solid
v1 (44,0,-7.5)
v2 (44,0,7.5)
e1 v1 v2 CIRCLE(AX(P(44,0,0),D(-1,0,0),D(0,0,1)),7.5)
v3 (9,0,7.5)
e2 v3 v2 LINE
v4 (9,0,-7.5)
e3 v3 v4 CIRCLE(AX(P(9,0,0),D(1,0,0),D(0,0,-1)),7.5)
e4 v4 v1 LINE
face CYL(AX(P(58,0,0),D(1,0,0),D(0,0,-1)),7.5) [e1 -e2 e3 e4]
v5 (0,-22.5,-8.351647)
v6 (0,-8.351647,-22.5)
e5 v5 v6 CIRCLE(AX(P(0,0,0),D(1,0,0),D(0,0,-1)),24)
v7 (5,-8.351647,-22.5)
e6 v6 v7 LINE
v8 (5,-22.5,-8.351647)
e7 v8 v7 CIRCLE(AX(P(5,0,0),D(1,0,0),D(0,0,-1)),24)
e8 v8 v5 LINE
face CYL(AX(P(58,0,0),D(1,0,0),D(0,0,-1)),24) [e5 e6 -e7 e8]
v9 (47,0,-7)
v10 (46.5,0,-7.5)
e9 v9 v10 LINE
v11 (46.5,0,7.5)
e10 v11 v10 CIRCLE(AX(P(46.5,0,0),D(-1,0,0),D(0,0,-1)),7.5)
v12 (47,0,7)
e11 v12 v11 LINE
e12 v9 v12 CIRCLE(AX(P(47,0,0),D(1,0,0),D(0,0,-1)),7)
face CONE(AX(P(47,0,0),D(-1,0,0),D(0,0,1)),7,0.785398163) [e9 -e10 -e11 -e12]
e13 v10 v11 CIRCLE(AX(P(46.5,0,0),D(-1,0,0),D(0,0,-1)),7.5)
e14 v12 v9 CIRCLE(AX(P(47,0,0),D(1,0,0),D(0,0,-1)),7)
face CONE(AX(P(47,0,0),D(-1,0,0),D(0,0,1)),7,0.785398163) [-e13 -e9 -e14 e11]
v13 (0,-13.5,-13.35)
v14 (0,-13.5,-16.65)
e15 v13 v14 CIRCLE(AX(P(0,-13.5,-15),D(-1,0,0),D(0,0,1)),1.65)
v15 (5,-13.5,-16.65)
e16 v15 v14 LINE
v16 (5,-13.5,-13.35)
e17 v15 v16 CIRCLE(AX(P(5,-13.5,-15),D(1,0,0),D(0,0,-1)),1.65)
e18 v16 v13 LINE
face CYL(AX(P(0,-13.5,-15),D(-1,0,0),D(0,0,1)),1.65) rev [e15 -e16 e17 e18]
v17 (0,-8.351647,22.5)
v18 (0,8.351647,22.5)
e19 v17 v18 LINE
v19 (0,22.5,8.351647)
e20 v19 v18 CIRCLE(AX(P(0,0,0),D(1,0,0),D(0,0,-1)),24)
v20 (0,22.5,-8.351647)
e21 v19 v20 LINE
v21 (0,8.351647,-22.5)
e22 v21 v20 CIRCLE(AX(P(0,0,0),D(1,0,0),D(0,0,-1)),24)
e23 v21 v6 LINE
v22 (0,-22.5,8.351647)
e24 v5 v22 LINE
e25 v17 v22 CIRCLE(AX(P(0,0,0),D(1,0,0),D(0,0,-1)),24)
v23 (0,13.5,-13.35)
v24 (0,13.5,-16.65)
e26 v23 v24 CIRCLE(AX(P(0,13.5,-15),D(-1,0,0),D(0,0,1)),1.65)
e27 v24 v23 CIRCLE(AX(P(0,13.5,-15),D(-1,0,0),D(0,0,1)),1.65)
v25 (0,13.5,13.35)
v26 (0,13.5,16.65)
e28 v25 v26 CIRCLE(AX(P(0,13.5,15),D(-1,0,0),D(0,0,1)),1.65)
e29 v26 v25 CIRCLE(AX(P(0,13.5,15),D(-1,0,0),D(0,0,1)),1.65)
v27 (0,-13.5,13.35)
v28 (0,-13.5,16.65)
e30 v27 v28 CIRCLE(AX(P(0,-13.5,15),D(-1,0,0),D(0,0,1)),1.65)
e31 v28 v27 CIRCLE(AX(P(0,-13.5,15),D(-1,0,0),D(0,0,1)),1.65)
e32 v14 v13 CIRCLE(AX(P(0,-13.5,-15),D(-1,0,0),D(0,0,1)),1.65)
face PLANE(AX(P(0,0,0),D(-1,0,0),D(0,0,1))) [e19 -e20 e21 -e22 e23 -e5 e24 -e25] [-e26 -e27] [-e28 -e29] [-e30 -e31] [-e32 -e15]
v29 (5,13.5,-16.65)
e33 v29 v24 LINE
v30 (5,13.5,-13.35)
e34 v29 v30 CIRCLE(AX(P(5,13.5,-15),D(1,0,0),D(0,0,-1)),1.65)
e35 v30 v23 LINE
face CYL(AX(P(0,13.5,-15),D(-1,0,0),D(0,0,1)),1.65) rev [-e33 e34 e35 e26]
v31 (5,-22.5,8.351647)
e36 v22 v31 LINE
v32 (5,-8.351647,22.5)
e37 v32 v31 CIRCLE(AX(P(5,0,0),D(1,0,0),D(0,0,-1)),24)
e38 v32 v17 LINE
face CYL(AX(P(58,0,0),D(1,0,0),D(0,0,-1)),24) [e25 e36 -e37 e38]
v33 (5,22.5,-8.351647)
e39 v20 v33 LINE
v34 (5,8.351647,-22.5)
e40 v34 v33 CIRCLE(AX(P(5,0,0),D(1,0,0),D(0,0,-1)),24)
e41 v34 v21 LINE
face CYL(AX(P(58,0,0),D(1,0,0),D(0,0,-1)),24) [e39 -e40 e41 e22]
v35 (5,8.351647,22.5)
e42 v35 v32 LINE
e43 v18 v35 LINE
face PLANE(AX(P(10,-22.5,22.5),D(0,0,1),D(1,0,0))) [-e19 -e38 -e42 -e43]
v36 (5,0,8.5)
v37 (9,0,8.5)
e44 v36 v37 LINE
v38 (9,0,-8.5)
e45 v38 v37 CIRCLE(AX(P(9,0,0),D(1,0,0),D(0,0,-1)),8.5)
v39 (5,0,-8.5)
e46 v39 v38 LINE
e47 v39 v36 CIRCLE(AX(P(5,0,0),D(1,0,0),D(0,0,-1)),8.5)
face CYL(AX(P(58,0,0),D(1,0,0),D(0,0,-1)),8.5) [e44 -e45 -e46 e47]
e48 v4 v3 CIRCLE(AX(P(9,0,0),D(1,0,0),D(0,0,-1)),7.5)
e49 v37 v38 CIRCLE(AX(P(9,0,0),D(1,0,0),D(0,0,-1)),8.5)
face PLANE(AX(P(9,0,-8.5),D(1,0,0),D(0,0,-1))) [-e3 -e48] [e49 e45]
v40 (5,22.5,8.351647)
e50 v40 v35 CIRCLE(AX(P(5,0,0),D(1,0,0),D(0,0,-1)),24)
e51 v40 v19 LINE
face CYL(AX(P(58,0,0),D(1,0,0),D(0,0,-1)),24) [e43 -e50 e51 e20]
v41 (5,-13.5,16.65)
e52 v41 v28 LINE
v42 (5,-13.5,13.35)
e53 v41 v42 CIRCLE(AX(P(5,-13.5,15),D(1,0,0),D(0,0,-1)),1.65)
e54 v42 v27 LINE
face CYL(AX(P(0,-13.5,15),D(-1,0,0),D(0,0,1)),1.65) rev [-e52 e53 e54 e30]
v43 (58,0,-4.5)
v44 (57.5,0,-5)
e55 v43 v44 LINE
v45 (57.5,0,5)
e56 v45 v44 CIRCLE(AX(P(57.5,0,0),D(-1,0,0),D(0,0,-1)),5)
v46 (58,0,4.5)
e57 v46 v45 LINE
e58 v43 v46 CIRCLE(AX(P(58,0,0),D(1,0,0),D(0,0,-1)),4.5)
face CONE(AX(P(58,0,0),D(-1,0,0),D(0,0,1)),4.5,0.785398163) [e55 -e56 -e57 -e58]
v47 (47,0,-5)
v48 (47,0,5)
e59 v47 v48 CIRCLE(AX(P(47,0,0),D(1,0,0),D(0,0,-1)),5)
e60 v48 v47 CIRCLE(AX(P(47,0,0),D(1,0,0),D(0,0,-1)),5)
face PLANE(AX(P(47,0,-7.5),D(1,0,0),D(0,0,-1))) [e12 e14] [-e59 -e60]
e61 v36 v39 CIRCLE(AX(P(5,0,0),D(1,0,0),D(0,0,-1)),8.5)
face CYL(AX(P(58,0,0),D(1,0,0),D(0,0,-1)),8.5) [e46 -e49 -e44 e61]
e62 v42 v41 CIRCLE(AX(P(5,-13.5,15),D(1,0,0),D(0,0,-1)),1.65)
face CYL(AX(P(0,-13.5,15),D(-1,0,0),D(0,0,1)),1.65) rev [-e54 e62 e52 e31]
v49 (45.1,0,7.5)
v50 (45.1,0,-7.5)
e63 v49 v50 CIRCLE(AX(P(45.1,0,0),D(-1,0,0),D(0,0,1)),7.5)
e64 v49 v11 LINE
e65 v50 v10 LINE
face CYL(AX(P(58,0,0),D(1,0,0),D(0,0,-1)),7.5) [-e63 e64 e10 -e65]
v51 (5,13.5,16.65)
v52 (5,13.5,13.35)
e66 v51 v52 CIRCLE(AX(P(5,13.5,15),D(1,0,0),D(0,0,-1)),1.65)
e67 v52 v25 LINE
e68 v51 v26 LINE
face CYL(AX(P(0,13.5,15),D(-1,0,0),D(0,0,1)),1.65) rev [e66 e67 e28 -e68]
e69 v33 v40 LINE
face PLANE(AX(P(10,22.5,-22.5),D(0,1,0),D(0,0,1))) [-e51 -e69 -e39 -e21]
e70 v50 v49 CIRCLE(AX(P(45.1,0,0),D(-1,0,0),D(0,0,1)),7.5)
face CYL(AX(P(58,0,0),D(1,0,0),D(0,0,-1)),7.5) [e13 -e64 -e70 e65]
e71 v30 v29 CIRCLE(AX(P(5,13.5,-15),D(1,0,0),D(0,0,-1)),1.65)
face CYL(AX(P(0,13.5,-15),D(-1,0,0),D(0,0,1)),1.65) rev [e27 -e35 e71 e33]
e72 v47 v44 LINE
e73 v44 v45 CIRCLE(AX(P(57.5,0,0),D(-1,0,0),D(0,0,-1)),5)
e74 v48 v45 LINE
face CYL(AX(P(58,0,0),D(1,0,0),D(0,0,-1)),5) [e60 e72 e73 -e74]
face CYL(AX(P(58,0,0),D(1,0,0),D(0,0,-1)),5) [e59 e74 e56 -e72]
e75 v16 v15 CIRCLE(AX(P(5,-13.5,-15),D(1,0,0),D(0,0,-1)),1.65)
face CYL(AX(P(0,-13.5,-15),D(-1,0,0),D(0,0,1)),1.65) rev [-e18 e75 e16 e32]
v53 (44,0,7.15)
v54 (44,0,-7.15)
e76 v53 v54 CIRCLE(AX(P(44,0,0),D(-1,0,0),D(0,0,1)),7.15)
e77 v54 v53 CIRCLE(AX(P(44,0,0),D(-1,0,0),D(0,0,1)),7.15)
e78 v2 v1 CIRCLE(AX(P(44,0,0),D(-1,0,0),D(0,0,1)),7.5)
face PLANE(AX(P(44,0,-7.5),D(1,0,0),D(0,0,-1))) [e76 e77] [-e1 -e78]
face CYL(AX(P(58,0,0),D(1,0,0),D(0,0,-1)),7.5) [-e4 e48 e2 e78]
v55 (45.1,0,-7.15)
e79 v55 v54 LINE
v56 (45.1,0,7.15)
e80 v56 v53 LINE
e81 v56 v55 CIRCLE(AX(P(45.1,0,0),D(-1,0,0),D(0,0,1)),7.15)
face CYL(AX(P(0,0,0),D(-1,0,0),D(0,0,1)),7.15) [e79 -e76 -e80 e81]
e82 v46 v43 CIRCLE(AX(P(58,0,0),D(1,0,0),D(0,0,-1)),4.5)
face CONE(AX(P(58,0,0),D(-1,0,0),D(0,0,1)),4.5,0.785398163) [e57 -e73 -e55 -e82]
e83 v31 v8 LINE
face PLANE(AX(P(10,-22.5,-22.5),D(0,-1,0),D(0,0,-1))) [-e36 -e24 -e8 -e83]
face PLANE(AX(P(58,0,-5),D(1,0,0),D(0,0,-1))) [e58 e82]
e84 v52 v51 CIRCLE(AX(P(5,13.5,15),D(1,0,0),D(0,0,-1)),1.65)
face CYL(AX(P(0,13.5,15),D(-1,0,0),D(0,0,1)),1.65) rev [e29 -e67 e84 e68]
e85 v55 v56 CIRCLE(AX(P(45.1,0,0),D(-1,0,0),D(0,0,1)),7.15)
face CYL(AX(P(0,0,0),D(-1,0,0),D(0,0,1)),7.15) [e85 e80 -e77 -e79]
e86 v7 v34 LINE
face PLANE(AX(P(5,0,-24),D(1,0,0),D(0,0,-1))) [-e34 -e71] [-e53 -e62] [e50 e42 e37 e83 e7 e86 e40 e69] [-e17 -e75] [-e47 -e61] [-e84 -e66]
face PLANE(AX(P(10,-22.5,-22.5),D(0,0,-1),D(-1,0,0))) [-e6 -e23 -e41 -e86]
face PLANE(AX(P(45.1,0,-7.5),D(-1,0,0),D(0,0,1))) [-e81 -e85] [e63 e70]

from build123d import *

# Parameters (mm, degrees)
HOLE_WIZARD_M4_1_D   = 3.3
SKETCH_4_OUTSIDE_W   = 67.858
SKETCH_4_OUTSIDE_H   = 67.858
SKETCH_4_OUTSIDE_W_2 = 45
SKETCH_4_OUTSIDE_H_2 = 45
CUT_EXTRUDE_1_DEPTH  = 10
CHAMFER_1_SIZE       = 0.5
SKETCH_5_W           = 1.1
SKETCH_5_H           = 0.35


with BuildPart() as part:
    # 草图1 → 旋转1 (revolve)
    with BuildSketch(Plane(origin=(0, 0, 0), x_dir=(1, 0, 0), z_dir=(0, 1, 0))):
        Polygon((0, 0), (0, 24), (5, 24), (5, 8.5), (9, 8.5), (9, 7.5), (47, 7.5), (47, 5), (58, 5), (58, 0), align=None)
    revolve(axis=Axis((58, 0, 0), (-1, 0, 0)))

    # M4 螺纹孔1 (through all)
    with Locations(Plane(origin=(0, 13.5, -15), x_dir=(0, 0, -1), z_dir=(-1, 0, 0))):
        with Locations((0, 0), (-30, 0), (0, 27), (-30, 27)):
            Hole(HOLE_WIZARD_M4_1_D / 2)

    # 草图4 outside → 切除-拉伸1 (cut)
    with BuildSketch(Plane.ZY):
        Rectangle(SKETCH_4_OUTSIDE_W, SKETCH_4_OUTSIDE_H)
        Rectangle(SKETCH_4_OUTSIDE_W_2, SKETCH_4_OUTSIDE_H_2, mode=Mode.SUBTRACT)
    extrude(amount=-CUT_EXTRUDE_1_DEPTH, mode=Mode.SUBTRACT)

    # 倒角1
    chamfer_1_edges = [part.edges().sort_by_distance(p)[0] for p in [
        (58, 0, 5),
        (47, 0, 7.5),
    ]]
    chamfer(chamfer_1_edges, length=CHAMFER_1_SIZE)

    # 草图5 → 切除-旋转1 (revolve, cut)
    with BuildSketch(Plane(origin=(0, 0, 0), x_dir=(1, 0, 0), z_dir=(0, 1, 0))):
        with Locations((44.55, 7.325)):
            Rectangle(SKETCH_5_W, SKETCH_5_H)
    revolve(axis=Axis((0, 0, 0), (1, 0, 0)), mode=Mode.SUBTRACT)


solid = part.part
